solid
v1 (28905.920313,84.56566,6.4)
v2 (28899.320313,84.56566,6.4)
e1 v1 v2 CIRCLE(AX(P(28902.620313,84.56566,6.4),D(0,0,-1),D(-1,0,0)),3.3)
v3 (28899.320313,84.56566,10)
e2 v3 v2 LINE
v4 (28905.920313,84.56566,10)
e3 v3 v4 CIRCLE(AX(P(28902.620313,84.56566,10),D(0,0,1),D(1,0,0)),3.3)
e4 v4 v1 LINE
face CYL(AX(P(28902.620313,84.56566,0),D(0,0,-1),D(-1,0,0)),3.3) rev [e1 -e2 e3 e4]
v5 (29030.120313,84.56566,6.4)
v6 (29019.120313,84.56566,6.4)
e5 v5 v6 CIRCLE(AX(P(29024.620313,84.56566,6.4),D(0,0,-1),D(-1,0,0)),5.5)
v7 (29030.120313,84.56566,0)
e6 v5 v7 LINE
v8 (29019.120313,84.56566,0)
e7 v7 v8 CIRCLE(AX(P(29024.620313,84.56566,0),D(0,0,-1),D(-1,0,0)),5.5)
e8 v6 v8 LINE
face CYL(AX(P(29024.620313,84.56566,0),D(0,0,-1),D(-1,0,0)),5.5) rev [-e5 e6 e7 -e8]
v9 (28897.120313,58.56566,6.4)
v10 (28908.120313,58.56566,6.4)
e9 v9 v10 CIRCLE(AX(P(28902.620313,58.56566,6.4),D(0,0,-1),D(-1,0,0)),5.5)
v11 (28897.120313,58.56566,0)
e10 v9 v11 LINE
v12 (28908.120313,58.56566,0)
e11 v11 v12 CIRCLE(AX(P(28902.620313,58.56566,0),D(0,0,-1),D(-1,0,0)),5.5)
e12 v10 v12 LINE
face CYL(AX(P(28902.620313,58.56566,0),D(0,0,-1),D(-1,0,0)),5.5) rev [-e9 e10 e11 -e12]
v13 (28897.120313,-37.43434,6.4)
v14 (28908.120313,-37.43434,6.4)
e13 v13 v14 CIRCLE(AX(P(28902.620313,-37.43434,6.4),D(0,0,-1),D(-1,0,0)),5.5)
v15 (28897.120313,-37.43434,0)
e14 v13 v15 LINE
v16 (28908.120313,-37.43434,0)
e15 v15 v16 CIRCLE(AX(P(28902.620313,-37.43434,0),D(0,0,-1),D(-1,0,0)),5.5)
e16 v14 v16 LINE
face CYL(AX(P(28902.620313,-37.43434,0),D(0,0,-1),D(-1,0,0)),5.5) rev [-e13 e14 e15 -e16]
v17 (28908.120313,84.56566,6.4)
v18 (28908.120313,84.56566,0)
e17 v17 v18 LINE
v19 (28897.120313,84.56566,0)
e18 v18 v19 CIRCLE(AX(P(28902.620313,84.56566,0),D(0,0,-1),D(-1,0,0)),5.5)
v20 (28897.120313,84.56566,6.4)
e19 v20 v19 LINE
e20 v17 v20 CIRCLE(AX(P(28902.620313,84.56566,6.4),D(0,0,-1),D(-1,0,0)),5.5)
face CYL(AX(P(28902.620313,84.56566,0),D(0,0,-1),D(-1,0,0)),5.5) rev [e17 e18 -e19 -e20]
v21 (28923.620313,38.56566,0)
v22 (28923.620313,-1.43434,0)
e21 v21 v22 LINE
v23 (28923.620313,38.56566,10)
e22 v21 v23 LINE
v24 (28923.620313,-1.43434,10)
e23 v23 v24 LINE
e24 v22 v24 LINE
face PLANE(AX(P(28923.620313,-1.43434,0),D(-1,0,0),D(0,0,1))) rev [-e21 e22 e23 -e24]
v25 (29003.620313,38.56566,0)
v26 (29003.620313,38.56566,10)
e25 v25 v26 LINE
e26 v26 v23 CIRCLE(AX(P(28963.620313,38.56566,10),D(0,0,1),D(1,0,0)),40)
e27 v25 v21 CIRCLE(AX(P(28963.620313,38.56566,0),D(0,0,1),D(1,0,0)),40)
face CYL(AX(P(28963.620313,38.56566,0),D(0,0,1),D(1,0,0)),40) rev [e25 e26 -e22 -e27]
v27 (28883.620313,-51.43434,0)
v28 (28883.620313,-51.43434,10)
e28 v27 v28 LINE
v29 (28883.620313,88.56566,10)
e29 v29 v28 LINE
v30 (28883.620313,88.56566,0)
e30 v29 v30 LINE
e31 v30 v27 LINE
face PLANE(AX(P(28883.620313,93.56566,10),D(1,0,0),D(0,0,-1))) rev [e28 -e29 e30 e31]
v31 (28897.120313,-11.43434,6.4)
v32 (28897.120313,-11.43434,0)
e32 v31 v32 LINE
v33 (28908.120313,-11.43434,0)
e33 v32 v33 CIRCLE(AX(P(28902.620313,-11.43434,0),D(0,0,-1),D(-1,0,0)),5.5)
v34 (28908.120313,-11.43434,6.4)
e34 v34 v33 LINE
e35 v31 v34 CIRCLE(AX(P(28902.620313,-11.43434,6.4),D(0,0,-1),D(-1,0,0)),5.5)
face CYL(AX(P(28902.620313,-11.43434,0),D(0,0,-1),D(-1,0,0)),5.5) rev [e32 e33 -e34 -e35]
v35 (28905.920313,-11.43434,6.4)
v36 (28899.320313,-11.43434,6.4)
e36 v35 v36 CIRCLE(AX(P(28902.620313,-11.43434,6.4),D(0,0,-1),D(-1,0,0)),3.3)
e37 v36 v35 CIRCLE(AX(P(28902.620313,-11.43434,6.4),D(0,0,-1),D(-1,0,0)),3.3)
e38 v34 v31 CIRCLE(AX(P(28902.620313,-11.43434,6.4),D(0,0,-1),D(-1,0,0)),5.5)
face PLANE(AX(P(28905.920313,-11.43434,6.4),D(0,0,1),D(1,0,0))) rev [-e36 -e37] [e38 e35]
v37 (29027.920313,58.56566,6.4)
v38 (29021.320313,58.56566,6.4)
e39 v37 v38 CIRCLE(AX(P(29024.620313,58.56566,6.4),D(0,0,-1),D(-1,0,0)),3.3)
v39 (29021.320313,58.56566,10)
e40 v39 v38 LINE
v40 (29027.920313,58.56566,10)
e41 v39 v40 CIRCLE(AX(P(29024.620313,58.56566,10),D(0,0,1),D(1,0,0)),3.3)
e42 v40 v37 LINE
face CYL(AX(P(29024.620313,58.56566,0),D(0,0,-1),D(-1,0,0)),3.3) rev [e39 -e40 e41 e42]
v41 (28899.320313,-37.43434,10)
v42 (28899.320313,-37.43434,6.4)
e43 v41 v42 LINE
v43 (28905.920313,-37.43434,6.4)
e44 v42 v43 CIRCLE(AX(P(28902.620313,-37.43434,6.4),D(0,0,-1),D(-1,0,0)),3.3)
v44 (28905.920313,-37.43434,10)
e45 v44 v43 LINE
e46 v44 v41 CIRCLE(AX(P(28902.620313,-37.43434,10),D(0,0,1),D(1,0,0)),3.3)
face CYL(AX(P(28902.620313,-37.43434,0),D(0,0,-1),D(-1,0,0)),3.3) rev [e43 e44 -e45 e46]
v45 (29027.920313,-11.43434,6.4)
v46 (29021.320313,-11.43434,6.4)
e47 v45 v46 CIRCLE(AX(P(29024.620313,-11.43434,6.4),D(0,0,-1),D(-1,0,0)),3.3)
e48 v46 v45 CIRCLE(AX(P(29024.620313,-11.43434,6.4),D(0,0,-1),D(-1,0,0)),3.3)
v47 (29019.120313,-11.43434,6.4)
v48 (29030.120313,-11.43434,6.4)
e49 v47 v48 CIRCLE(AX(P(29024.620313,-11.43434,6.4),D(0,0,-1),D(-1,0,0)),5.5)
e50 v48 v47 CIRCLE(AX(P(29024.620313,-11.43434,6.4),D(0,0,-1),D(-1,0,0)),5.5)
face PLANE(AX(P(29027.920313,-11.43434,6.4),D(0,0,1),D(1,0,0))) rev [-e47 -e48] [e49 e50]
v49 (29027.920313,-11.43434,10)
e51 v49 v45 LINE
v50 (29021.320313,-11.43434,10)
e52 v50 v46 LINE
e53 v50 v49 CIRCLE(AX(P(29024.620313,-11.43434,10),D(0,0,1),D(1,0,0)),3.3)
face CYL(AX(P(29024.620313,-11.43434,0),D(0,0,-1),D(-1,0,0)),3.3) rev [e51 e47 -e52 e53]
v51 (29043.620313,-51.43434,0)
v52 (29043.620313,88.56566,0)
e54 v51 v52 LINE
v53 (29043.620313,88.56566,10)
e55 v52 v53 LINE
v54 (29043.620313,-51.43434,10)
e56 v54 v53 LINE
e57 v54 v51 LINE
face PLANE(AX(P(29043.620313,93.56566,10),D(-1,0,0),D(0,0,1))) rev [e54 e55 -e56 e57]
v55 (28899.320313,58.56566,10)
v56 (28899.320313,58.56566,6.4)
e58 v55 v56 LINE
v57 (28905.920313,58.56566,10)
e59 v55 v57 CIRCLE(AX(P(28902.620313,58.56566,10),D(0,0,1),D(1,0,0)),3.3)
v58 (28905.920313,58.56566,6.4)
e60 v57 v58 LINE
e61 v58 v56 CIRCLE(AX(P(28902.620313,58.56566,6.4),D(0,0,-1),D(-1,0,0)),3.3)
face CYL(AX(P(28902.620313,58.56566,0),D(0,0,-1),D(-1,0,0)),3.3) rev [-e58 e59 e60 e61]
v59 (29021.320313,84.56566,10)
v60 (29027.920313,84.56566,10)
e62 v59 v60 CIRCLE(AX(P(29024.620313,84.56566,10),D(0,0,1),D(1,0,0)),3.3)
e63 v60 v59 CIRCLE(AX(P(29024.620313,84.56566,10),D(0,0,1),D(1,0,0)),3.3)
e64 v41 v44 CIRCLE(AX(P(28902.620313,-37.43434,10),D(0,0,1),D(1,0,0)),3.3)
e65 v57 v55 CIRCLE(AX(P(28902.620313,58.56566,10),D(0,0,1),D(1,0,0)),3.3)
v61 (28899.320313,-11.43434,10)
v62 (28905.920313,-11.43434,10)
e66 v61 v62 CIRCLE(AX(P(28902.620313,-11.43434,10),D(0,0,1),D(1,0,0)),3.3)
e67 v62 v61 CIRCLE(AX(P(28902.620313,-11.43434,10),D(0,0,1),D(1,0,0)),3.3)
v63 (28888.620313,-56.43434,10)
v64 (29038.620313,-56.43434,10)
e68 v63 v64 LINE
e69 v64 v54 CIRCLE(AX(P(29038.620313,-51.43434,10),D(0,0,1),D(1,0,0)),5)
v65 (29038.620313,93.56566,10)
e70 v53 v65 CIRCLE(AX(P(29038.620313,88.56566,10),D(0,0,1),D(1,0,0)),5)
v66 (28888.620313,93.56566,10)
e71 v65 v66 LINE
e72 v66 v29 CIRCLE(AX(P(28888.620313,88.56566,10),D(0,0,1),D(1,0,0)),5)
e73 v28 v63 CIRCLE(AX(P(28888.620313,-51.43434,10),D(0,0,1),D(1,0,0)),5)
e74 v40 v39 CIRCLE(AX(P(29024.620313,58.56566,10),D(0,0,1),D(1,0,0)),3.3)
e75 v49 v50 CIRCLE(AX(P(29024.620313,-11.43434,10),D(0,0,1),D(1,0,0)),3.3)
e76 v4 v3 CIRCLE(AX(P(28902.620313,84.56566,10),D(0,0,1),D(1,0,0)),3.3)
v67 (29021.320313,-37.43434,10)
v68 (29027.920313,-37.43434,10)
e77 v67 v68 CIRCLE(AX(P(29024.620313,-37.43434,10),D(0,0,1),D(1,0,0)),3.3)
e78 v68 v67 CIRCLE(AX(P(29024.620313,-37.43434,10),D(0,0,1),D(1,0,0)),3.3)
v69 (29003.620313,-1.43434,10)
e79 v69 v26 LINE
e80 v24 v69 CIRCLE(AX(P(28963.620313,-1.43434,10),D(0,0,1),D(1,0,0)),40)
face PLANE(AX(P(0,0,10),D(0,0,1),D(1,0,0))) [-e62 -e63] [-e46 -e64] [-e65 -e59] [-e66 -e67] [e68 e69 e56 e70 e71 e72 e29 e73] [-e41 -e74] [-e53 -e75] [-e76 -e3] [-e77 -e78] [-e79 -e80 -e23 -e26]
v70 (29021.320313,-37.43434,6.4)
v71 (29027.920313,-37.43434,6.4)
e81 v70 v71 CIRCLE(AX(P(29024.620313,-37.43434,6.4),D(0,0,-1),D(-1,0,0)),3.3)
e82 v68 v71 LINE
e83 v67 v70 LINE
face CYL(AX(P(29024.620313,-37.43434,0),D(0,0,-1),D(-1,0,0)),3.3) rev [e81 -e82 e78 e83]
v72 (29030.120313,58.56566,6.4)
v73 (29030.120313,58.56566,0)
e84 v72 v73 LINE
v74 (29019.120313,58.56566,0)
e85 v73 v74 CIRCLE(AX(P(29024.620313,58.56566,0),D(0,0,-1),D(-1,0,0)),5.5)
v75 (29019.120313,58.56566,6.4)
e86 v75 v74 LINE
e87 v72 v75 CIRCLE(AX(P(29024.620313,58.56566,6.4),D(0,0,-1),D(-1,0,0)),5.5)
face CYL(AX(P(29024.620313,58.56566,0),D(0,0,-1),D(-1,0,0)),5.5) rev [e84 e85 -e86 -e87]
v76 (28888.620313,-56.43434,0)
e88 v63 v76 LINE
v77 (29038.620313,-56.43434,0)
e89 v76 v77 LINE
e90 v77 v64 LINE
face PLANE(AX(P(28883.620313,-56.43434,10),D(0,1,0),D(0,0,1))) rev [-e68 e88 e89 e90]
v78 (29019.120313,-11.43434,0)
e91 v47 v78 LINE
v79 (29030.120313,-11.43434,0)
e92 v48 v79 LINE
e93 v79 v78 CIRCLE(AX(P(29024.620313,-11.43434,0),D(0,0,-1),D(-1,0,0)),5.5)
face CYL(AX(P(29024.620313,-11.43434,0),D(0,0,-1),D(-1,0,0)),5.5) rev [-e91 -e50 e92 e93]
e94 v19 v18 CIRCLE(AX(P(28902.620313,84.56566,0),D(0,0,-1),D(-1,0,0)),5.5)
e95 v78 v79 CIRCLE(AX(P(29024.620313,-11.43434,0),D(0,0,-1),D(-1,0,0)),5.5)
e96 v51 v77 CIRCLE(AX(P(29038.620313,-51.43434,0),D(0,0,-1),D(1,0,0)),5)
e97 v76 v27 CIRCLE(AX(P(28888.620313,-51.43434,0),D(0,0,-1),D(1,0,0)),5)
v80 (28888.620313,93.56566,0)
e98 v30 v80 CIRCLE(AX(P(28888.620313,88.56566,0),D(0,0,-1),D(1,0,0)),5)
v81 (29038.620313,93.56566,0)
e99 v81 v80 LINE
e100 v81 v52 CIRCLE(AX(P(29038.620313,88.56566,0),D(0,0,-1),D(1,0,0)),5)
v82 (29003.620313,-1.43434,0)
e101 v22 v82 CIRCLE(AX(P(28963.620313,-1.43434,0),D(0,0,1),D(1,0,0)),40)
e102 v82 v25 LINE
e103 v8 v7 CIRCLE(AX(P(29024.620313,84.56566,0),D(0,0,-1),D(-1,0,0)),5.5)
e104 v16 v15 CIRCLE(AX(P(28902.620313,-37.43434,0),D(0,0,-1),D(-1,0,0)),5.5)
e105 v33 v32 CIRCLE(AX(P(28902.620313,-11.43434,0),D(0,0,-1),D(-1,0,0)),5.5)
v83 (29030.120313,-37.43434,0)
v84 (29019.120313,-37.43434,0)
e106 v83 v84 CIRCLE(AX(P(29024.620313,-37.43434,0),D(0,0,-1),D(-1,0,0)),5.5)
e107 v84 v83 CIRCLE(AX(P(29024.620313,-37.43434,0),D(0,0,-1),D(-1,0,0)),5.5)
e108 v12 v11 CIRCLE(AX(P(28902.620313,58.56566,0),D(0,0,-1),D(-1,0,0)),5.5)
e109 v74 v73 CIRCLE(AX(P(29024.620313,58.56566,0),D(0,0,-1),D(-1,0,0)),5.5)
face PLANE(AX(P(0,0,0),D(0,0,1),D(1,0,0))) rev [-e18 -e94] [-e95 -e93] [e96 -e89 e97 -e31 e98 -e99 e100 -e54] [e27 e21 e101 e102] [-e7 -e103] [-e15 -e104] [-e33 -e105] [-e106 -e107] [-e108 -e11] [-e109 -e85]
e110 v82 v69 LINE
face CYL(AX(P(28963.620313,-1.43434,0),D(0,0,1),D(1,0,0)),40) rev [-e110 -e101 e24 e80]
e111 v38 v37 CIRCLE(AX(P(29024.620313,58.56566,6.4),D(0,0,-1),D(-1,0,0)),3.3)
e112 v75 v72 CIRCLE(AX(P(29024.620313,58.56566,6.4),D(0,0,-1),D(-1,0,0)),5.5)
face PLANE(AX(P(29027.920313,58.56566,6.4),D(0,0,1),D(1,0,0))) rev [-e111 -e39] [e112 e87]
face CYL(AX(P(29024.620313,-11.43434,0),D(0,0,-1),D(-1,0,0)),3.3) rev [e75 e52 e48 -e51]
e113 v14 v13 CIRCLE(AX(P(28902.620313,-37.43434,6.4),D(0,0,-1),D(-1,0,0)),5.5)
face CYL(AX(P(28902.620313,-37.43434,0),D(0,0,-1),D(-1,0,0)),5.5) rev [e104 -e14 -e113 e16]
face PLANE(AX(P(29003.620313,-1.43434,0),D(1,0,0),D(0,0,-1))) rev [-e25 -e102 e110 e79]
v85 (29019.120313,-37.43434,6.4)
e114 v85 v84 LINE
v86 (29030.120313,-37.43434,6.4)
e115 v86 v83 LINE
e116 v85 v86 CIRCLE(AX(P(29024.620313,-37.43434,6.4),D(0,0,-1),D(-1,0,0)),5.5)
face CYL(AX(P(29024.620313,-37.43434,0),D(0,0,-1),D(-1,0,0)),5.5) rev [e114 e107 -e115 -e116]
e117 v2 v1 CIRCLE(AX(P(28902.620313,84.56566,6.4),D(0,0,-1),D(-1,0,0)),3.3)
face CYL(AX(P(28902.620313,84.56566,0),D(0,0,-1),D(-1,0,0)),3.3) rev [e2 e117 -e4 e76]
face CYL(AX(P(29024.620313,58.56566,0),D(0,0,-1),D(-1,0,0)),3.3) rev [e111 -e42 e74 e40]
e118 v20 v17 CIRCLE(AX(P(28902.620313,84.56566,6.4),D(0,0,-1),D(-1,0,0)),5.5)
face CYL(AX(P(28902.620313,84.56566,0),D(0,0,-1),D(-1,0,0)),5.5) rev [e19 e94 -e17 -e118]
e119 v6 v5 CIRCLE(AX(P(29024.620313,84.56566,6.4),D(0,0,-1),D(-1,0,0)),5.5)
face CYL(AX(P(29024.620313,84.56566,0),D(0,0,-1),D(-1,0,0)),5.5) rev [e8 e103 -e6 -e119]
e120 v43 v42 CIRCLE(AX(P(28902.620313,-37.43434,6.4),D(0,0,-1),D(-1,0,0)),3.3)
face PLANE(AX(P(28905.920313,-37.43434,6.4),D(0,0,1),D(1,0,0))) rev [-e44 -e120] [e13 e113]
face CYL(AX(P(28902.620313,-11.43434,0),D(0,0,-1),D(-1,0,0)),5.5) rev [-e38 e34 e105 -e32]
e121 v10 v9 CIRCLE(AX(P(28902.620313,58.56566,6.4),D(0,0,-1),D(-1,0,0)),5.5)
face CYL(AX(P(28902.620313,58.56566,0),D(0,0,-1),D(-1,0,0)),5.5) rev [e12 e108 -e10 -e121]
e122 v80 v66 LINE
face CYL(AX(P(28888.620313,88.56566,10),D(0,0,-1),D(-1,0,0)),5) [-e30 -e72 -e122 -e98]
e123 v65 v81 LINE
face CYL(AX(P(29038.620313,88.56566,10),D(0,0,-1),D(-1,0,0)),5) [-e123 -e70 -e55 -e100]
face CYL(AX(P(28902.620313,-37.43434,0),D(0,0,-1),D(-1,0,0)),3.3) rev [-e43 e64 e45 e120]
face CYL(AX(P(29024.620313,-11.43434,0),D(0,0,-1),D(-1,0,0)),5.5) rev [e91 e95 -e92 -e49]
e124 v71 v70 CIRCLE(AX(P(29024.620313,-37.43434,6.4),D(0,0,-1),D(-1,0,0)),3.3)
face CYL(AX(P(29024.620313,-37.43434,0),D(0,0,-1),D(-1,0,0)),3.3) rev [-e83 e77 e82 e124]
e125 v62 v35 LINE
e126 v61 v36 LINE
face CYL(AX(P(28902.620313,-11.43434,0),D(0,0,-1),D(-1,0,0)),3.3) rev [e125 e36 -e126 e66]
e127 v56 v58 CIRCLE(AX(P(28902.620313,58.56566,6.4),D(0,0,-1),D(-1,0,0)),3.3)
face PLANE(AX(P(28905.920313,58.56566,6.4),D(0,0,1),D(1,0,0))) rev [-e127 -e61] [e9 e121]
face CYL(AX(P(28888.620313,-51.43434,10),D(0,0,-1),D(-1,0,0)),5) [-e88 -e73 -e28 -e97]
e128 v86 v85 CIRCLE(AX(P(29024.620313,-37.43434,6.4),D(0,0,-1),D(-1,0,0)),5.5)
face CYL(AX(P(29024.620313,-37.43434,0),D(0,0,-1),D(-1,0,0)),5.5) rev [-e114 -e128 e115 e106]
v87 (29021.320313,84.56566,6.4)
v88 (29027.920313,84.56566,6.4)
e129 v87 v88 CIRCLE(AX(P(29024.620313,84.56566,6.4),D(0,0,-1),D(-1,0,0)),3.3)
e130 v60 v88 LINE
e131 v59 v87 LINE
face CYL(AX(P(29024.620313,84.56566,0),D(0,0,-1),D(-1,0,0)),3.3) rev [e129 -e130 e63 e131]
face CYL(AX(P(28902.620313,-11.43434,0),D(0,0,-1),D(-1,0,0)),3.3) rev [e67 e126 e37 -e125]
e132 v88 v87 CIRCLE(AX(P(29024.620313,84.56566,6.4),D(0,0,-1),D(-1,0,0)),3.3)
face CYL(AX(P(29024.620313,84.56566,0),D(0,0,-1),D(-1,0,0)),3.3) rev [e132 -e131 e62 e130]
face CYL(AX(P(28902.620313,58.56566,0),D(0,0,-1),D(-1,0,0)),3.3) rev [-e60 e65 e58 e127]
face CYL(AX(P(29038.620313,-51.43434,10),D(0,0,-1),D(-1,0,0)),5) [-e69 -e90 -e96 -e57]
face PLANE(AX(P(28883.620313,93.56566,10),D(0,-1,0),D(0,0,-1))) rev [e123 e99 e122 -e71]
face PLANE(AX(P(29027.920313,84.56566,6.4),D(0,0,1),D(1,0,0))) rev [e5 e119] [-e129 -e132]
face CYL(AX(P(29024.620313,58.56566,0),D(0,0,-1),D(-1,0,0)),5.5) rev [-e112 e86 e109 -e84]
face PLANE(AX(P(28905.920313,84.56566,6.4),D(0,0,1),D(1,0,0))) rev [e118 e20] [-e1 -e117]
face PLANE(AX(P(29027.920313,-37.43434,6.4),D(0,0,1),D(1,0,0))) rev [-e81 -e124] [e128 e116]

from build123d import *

# Parameters (mm, degrees)
SKETCH_1_W                   = 160
SKETCH_1_H                   = 150
EXTRUDE_1_DEPTH              = 10
FILLET_1_R                   = 5
HOLE_WIZARD_M6_1_D           = 6.6
HOLE_WIZARD_M6_1_DEPTH       = 11.5
HOLE_WIZARD_M6_1_CBORE_D     = 11
HOLE_WIZARD_M6_1_CBORE_DEPTH = 6.4
HOLE_WIZARD_M6_1_TIP         = 1.982840043
CUT_EXTRUDE_1_DEPTH          = 10


with BuildPart() as part:
    # 草图1 → 凸台-拉伸1 (new body)
    with BuildSketch(Plane.XY):
        with Locations((28963.620313483, 18.565660066)):
            Rectangle(SKETCH_1_W, SKETCH_1_H)
    extrude(amount=EXTRUDE_1_DEPTH)

    # 圆角1
    fillet_1_edges = [part.edges().sort_by_distance(p)[0] for p in [
        (28883.620313483, 93.565660066, 5),
        (29043.620313483, 93.565660066, 5),
        (29043.620313483, -56.434339934, 5),
        (28883.620313483, -56.434339934, 5),
    ]]
    fillet(fillet_1_edges, radius=FILLET_1_R)

    # M6 六角凹头螺钉的柱形沉头孔1
    with Locations(Plane(origin=(0, 0, 0), x_dir=(-1, 0, 0), z_dir=(0, 0, -1))):
        with Locations((-29024.620313483, 84.565660077), (-29024.620313483, 58.565660077), (-29024.620313483, -11.434339923), (-29024.620313483, -37.434339923), (-28902.620313482, -37.434339923), (-28902.620313482, -11.434339923), (-28902.620313482, 58.565660077), (-28902.620313482, 84.565660077)):
            CounterBoreHole(HOLE_WIZARD_M6_1_D / 2, HOLE_WIZARD_M6_1_CBORE_D / 2, HOLE_WIZARD_M6_1_CBORE_DEPTH, depth=HOLE_WIZARD_M6_1_DEPTH)
            with Locations((0, 0, -(HOLE_WIZARD_M6_1_DEPTH + HOLE_WIZARD_M6_1_TIP / 2))):  # 118° drill point
                Cone(0, HOLE_WIZARD_M6_1_D / 2, HOLE_WIZARD_M6_1_TIP, mode=Mode.SUBTRACT)

    # 草图4 → 切除-拉伸1 (cut)
    with BuildSketch(Plane.XY.offset(10)):
        with BuildLine():
            Line((28923.620313483, -1.434339933), (28923.620313483, 38.565660067))
            ThreePointArc((28923.620313483, 38.565660067), (28963.620313483, 78.565660067), (29003.620313483, 38.565660067))
            Line((29003.620313483, 38.565660067), (29003.620313483, -1.434339933))
            ThreePointArc((29003.620313483, -1.434339933), (28963.620313483, -41.434339933), (28923.620313483, -1.434339933))
        make_face()
    extrude(amount=-CUT_EXTRUDE_1_DEPTH, mode=Mode.SUBTRACT)


solid = part.part
